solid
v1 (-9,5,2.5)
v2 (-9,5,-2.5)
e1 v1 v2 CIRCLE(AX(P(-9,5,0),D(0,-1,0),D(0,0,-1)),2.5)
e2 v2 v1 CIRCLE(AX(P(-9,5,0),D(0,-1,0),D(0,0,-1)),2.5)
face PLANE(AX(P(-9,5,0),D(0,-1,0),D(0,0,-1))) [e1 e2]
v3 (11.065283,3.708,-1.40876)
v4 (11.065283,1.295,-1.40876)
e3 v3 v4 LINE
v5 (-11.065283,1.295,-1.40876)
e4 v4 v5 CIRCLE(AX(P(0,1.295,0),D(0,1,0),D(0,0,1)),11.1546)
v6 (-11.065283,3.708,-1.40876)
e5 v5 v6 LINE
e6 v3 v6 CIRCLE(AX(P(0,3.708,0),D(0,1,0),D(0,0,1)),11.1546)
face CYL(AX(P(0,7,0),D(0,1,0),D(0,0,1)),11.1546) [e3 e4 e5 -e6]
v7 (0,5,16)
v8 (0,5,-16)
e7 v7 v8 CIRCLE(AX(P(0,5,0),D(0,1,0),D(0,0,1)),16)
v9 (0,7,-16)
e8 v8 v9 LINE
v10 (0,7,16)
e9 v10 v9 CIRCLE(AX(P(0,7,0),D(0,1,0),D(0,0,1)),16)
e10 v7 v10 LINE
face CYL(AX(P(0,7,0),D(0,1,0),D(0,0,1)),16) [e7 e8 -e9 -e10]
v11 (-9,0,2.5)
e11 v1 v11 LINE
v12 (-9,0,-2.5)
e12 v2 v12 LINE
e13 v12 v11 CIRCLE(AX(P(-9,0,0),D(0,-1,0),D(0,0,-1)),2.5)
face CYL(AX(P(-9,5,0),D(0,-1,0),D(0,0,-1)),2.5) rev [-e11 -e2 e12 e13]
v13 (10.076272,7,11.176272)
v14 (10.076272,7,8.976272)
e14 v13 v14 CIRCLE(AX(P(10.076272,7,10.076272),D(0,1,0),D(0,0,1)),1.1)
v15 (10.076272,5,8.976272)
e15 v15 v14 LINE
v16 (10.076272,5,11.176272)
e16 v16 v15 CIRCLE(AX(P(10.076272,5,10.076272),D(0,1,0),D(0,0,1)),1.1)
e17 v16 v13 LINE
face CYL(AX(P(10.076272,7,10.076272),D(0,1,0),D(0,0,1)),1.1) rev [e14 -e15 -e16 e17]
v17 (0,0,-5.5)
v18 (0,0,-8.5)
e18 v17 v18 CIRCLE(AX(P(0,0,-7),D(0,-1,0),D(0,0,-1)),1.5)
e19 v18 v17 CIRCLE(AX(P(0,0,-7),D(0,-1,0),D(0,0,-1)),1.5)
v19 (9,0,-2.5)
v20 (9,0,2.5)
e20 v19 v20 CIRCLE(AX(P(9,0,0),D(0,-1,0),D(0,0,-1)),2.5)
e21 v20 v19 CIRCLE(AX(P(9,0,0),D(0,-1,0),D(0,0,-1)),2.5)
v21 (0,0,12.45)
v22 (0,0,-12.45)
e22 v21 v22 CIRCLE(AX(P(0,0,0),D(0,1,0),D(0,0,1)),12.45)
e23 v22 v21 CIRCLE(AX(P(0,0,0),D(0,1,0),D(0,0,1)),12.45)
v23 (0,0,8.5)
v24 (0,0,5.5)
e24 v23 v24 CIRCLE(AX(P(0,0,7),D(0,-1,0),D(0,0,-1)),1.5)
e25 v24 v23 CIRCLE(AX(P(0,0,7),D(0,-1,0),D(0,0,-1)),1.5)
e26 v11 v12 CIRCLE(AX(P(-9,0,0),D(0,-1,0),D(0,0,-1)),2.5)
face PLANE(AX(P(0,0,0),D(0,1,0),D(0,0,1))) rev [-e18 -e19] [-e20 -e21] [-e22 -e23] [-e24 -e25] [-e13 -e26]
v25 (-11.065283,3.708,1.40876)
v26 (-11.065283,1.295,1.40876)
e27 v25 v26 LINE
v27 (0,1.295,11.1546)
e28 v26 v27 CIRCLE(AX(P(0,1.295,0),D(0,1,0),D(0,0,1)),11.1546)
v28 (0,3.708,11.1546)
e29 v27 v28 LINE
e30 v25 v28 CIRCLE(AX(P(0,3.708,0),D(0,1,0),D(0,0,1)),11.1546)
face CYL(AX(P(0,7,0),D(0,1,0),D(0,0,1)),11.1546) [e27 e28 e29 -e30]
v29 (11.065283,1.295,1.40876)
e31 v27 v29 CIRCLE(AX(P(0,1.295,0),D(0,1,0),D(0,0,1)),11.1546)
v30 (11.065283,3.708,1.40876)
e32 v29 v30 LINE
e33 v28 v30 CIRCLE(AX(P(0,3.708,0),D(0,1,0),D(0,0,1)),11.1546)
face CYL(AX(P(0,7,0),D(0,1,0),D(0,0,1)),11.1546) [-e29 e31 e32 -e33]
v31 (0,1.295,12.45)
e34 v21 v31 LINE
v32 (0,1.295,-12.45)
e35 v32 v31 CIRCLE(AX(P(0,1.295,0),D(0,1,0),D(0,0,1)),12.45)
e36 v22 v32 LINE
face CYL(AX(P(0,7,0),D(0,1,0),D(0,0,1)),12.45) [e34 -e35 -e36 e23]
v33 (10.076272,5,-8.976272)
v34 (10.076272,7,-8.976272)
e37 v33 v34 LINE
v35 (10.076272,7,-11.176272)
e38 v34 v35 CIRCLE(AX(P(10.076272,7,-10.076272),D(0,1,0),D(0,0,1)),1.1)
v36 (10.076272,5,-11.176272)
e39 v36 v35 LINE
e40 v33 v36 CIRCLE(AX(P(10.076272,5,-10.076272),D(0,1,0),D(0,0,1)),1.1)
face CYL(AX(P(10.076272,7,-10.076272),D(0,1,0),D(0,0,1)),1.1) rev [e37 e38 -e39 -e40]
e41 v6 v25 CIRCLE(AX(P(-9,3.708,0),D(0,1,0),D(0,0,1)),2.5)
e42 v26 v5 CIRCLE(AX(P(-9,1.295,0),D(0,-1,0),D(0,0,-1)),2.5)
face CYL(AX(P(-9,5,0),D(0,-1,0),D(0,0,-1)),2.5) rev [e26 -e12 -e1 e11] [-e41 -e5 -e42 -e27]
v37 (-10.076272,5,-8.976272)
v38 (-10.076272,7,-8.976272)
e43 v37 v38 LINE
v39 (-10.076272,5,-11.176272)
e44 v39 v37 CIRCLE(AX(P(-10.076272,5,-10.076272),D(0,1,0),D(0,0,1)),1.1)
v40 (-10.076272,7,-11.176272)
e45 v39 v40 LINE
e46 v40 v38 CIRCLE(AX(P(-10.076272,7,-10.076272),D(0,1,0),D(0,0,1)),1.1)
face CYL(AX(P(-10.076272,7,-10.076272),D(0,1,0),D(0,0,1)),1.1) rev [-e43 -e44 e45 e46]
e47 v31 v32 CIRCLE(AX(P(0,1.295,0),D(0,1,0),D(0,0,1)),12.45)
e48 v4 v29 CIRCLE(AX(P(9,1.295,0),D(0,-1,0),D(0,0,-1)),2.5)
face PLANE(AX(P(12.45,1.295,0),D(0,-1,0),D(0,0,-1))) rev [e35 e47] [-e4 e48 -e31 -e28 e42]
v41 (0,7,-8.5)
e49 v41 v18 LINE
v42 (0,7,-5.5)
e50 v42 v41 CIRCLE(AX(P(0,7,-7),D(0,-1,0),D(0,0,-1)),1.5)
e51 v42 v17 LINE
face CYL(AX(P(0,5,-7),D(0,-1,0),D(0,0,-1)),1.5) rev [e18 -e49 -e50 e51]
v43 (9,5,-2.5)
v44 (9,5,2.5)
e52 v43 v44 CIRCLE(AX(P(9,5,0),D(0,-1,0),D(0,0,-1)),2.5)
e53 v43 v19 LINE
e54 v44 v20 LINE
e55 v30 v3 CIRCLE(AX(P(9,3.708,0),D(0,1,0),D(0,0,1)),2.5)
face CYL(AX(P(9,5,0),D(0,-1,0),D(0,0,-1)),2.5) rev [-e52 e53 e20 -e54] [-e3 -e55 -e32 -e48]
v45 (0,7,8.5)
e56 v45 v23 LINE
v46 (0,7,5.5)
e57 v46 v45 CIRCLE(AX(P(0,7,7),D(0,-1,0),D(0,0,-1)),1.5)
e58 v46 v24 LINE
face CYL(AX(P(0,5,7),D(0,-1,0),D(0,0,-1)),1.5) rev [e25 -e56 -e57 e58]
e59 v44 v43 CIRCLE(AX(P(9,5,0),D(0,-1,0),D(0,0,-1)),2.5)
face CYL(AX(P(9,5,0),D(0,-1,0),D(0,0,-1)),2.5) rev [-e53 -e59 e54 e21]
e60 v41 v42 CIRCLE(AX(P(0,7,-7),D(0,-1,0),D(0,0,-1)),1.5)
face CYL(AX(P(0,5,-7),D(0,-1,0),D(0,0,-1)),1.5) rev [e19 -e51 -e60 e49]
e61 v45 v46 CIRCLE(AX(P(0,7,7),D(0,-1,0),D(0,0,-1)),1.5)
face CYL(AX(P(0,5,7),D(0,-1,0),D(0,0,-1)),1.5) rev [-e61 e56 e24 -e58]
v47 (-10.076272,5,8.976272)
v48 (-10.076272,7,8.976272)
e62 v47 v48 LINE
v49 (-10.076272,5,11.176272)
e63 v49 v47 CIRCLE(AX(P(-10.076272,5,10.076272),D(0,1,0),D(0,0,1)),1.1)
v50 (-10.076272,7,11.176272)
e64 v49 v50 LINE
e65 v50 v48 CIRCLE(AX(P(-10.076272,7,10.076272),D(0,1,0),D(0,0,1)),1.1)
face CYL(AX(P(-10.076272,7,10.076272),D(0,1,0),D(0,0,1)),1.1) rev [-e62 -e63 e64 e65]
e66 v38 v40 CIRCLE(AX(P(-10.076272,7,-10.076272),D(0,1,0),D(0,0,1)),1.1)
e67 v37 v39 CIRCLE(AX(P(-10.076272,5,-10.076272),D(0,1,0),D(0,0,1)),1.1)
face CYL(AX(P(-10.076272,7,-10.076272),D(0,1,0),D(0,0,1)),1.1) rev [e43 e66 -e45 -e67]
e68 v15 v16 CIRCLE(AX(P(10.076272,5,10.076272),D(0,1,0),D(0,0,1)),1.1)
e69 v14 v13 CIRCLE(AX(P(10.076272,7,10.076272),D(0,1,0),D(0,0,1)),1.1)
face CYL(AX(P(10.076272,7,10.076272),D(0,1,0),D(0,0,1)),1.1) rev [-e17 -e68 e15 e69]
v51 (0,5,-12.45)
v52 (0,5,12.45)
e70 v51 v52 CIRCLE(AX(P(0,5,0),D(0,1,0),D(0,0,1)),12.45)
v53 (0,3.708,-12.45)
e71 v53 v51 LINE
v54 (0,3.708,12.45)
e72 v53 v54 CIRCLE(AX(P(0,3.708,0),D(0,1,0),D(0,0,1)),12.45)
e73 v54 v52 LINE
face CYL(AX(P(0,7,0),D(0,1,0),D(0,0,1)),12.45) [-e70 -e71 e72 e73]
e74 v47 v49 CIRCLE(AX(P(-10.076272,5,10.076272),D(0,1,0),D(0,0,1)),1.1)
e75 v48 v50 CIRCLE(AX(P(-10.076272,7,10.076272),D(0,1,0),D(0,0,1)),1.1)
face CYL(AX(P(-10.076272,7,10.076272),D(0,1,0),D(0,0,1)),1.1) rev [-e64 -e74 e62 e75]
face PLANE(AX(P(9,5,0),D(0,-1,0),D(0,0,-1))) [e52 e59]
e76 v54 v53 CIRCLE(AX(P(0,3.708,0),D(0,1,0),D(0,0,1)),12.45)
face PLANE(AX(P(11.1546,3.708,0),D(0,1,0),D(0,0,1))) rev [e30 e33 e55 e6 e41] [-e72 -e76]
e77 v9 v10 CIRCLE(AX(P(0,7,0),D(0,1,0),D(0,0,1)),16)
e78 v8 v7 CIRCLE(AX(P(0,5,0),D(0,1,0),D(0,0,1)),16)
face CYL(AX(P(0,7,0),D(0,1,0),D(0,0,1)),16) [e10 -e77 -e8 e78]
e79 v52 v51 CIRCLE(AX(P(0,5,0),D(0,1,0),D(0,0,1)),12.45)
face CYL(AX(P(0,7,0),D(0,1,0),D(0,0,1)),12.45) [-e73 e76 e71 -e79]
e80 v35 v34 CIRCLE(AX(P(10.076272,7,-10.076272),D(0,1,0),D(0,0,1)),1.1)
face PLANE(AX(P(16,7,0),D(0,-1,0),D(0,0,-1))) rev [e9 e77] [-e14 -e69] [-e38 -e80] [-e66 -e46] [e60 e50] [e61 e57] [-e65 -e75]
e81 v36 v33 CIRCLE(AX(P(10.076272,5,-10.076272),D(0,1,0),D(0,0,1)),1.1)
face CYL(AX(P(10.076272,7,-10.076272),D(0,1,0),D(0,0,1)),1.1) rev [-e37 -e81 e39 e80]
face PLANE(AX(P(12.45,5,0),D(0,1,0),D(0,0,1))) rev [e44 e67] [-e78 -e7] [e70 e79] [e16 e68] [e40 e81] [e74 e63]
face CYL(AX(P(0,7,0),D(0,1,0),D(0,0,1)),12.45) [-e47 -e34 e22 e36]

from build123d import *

# Parameters (mm, degrees)
MM_1_D              = 2.2
MM_1_DEPTH          = 7.1
MM_1_TIP            = 0.660946681
SKETCH_7_R          = 2.5
SKETCH_7_R_2        = 1.5
CUT_EXTRUDE_1_DEPTH = 5
SKETCH_8_R          = 1.5
CUT_EXTRUDE_2_DEPTH = 5


with BuildPart() as part:
    # 草图1 → 旋转1 (revolve)
    with BuildSketch(Plane.XY, mode=Mode.PRIVATE) as revolve_1_sk:
        Polygon((0, 0), (12.45, 0), (12.45, 1.295), (11.1546, 1.295), (11.1546, 3.708), (12.45, 3.708), (12.45, 5), (16, 5), (16, 7), (0, 7), align=None)
    revolve(revolve_1_sk.sketch.rotate(Axis((0, 7, 0), (0, -1, 0)), 90), axis=Axis((0, 7, 0), (0, -1, 0)))

    # 大小mm 暗销孔1
    with Locations(Plane(origin=(0, 7, 0), x_dir=(1, 0, 0), z_dir=(0, 1, 0))):
        with Locations((-10.076271632, -10.076271632), (-10.076271632, 10.076271632), (10.076271632, 10.076271632), (10.076271632, -10.076271632)):
            Hole(MM_1_D / 2, depth=MM_1_DEPTH)
            with Locations((0, 0, -(MM_1_DEPTH + MM_1_TIP / 2))):  # 118° drill point
                Cone(0, MM_1_D / 2, MM_1_TIP, mode=Mode.SUBTRACT)

    # 草图7 → 切除-拉伸1 (cut)
    with BuildSketch(Plane.XZ):
        with Locations(Location((-9, 0, 0), (0, 0, 270))):
            Circle(SKETCH_7_R)
        with Locations(Location((9, 0, 0), (0, 0, 270))):
            Circle(SKETCH_7_R)
        with Locations(Location((0, -7, 0), (0, 0, 270))):
            Circle(SKETCH_7_R_2)
        with Locations(Location((0, 7, 0), (0, 0, 270))):
            Circle(SKETCH_7_R_2)
    extrude(amount=-CUT_EXTRUDE_1_DEPTH, mode=Mode.SUBTRACT)

    # 草图8 → 切除-拉伸2 (cut)
    with BuildSketch(Plane.XZ.offset(-5)):
        with Locations(Location((0, 7, 0), (0, 0, 270))):
            Circle(SKETCH_8_R)
        with Locations(Location((0, -7, 0), (0, 0, 270))):
            Circle(SKETCH_8_R)
    extrude(amount=-CUT_EXTRUDE_2_DEPTH, mode=Mode.SUBTRACT)


solid = part.part
